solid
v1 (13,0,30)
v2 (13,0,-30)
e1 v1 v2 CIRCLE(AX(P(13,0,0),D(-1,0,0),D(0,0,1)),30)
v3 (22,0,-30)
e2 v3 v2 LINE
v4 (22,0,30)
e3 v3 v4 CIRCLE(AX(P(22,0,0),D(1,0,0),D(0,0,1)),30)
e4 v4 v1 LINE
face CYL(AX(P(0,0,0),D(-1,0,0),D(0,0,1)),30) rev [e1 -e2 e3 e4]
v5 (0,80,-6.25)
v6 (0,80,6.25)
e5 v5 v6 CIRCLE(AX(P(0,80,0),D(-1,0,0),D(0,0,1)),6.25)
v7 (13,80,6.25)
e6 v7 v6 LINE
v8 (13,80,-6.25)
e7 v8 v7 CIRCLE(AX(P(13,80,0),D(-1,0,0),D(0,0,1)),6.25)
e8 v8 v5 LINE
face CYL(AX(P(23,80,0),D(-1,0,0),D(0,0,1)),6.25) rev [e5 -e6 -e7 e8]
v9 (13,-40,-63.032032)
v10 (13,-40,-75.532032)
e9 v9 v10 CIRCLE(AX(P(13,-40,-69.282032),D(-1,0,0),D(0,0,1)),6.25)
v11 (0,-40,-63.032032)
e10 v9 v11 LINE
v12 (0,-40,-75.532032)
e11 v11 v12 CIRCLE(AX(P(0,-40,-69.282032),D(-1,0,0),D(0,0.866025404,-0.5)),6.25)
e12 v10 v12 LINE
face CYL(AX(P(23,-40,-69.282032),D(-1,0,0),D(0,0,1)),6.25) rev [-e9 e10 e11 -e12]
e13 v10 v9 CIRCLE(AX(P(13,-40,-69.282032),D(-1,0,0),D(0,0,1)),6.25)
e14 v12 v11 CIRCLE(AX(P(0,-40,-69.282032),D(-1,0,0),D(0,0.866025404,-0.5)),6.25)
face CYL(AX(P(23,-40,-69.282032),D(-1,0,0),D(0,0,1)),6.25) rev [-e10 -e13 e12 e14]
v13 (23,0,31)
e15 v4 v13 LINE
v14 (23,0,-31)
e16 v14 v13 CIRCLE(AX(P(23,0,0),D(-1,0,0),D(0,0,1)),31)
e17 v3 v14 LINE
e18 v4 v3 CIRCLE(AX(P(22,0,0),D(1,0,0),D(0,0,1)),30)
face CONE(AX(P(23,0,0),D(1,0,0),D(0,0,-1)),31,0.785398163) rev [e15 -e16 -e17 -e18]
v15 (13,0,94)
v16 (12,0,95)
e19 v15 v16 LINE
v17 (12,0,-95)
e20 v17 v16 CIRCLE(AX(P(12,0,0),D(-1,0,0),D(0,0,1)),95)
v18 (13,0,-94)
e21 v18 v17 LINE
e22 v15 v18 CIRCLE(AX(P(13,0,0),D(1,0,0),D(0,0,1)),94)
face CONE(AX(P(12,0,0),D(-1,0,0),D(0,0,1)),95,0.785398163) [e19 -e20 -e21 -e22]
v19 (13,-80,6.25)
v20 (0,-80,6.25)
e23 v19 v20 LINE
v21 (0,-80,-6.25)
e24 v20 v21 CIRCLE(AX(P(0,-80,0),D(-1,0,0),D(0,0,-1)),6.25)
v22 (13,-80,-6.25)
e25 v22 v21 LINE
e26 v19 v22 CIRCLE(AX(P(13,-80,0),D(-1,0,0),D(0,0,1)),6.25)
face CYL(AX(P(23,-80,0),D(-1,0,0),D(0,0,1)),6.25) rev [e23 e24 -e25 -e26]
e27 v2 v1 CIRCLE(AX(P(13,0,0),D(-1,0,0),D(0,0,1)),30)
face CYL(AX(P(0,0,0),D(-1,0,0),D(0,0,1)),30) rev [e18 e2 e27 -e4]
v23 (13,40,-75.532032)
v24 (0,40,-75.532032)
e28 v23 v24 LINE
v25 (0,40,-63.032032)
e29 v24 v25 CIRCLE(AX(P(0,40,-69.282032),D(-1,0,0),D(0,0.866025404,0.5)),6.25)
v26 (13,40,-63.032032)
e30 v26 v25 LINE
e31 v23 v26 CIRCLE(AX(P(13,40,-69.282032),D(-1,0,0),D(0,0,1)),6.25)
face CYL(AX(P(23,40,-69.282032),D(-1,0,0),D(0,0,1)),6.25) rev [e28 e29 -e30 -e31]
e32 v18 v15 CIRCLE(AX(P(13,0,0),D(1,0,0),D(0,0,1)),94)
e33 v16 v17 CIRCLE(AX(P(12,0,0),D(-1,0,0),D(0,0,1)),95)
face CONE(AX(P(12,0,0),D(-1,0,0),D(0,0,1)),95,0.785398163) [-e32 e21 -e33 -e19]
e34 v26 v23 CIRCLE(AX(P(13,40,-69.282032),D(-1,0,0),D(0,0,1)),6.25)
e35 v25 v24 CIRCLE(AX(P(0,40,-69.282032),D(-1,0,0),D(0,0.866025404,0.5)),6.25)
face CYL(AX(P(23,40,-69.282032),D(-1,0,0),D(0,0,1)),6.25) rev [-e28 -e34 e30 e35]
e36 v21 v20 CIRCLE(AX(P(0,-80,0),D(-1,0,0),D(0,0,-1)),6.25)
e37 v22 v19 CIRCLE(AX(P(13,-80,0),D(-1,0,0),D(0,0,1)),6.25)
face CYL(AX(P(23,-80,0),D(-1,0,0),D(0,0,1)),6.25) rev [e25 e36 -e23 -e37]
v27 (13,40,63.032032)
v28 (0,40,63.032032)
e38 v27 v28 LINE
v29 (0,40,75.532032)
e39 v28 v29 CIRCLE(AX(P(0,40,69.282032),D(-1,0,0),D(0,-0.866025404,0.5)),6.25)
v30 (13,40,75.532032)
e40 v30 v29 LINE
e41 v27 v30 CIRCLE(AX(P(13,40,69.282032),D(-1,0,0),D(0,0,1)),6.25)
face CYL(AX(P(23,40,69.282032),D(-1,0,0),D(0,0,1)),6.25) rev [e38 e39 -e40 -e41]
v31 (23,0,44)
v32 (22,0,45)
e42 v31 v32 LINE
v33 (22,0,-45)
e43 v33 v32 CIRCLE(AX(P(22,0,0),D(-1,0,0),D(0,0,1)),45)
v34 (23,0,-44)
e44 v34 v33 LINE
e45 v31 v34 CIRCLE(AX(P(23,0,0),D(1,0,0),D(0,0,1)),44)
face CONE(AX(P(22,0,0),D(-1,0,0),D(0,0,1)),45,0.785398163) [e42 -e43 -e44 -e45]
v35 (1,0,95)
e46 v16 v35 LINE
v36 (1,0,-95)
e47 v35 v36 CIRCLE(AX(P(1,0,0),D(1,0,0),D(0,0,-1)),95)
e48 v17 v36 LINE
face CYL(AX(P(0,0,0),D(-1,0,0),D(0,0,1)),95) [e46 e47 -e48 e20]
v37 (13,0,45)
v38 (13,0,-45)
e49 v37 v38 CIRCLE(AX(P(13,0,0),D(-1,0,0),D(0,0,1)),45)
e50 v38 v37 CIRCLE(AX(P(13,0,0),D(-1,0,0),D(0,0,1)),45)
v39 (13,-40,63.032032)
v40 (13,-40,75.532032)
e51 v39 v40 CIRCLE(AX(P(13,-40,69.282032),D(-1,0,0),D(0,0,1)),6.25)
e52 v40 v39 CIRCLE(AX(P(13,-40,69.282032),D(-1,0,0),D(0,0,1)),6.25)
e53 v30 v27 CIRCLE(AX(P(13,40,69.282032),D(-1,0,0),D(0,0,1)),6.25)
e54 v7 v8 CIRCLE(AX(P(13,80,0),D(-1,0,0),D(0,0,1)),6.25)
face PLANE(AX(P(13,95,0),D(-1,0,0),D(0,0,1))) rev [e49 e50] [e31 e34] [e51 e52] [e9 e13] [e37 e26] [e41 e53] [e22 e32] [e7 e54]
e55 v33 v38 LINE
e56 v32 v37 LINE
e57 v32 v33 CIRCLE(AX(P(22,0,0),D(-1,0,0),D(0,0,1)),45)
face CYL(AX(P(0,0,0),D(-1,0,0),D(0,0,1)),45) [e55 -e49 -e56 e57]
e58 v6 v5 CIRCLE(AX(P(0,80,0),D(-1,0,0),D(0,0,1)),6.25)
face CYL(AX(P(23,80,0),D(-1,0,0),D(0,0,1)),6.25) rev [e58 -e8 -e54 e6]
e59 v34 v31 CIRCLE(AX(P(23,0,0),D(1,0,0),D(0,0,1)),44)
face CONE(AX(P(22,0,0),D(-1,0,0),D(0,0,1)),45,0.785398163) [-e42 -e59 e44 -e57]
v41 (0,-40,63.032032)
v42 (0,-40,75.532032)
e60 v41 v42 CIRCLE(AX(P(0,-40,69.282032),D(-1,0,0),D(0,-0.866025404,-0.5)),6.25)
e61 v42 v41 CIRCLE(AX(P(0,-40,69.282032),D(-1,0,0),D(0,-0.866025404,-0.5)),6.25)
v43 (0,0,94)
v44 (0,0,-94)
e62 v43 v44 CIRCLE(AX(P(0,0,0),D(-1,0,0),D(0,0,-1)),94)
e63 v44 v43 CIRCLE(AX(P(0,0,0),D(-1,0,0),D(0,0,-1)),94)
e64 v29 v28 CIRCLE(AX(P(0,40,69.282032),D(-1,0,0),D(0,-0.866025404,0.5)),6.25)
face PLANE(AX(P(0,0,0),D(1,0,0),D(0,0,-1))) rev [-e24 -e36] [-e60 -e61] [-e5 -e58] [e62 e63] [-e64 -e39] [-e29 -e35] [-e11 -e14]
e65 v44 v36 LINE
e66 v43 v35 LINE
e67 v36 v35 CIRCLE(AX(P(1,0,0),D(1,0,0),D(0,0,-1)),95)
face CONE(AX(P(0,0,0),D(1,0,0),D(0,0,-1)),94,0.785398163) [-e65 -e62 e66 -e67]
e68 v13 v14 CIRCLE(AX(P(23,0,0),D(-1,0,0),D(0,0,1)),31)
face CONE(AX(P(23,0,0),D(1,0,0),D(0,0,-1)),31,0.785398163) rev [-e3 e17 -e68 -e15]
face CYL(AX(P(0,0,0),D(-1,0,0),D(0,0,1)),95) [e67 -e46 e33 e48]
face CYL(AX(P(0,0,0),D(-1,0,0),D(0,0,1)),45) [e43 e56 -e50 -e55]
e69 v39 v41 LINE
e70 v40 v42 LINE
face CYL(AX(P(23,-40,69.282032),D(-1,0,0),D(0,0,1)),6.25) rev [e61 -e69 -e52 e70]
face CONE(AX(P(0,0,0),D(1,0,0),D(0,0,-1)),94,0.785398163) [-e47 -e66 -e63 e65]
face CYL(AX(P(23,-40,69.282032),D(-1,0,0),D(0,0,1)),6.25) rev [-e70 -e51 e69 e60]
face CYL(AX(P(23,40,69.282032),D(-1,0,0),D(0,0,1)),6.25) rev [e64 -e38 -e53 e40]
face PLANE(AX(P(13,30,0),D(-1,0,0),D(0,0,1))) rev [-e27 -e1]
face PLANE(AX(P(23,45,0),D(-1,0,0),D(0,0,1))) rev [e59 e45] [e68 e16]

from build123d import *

# Parameters (mm, degrees)
SKETCH_2_R               = 6.25
CUT_EXTRUDE_1_DEPTH      = 137.304805491
PATTERN_CIRCULAR_1_COUNT = 6
CHAMFER_1_SIZE           = 1


with BuildPart() as part:
    # 草图1 → 旋转1 (revolve)
    with BuildSketch(Plane.XY, mode=Mode.PRIVATE) as revolve_1_sk:
        Polygon((0, 0), (0, 95), (13, 95), (13, 45), (23, 45), (23, 30), (13, 30), (13, 0), align=None)
    revolve(revolve_1_sk.sketch.rotate(Axis((0, 0, 0), (1, 0, 0)), 90), axis=Axis((0, 0, 0), (1, 0, 0)))

    # 草图2 → 切除-拉伸1 (cut, through all)
    with BuildSketch(Plane.ZY):
        with Locations((0, 80)):
            Circle(SKETCH_2_R)
    cut_extrude_1 = extrude(amount=-CUT_EXTRUDE_1_DEPTH, mode=Mode.SUBTRACT)

    # 阵列(圆周)1: 切除-拉伸1 ×6 about axis
    pattern_circular_1_axis = Axis((0, 0, 0), (1, 0, 0))
    for i in range(1, PATTERN_CIRCULAR_1_COUNT):
        add(cut_extrude_1.rotate(pattern_circular_1_axis, i * 360 / PATTERN_CIRCULAR_1_COUNT), mode=Mode.SUBTRACT)

    # 倒角1
    chamfer_1_edges = [part.edges().sort_by_distance(p)[0] for p in [
        (23, 0, -30),
        (23, 0, -45),
        (13, 0, -95),
        (0, 0, -95),
    ]]
    chamfer(chamfer_1_edges, length=CHAMFER_1_SIZE)


solid = part.part
